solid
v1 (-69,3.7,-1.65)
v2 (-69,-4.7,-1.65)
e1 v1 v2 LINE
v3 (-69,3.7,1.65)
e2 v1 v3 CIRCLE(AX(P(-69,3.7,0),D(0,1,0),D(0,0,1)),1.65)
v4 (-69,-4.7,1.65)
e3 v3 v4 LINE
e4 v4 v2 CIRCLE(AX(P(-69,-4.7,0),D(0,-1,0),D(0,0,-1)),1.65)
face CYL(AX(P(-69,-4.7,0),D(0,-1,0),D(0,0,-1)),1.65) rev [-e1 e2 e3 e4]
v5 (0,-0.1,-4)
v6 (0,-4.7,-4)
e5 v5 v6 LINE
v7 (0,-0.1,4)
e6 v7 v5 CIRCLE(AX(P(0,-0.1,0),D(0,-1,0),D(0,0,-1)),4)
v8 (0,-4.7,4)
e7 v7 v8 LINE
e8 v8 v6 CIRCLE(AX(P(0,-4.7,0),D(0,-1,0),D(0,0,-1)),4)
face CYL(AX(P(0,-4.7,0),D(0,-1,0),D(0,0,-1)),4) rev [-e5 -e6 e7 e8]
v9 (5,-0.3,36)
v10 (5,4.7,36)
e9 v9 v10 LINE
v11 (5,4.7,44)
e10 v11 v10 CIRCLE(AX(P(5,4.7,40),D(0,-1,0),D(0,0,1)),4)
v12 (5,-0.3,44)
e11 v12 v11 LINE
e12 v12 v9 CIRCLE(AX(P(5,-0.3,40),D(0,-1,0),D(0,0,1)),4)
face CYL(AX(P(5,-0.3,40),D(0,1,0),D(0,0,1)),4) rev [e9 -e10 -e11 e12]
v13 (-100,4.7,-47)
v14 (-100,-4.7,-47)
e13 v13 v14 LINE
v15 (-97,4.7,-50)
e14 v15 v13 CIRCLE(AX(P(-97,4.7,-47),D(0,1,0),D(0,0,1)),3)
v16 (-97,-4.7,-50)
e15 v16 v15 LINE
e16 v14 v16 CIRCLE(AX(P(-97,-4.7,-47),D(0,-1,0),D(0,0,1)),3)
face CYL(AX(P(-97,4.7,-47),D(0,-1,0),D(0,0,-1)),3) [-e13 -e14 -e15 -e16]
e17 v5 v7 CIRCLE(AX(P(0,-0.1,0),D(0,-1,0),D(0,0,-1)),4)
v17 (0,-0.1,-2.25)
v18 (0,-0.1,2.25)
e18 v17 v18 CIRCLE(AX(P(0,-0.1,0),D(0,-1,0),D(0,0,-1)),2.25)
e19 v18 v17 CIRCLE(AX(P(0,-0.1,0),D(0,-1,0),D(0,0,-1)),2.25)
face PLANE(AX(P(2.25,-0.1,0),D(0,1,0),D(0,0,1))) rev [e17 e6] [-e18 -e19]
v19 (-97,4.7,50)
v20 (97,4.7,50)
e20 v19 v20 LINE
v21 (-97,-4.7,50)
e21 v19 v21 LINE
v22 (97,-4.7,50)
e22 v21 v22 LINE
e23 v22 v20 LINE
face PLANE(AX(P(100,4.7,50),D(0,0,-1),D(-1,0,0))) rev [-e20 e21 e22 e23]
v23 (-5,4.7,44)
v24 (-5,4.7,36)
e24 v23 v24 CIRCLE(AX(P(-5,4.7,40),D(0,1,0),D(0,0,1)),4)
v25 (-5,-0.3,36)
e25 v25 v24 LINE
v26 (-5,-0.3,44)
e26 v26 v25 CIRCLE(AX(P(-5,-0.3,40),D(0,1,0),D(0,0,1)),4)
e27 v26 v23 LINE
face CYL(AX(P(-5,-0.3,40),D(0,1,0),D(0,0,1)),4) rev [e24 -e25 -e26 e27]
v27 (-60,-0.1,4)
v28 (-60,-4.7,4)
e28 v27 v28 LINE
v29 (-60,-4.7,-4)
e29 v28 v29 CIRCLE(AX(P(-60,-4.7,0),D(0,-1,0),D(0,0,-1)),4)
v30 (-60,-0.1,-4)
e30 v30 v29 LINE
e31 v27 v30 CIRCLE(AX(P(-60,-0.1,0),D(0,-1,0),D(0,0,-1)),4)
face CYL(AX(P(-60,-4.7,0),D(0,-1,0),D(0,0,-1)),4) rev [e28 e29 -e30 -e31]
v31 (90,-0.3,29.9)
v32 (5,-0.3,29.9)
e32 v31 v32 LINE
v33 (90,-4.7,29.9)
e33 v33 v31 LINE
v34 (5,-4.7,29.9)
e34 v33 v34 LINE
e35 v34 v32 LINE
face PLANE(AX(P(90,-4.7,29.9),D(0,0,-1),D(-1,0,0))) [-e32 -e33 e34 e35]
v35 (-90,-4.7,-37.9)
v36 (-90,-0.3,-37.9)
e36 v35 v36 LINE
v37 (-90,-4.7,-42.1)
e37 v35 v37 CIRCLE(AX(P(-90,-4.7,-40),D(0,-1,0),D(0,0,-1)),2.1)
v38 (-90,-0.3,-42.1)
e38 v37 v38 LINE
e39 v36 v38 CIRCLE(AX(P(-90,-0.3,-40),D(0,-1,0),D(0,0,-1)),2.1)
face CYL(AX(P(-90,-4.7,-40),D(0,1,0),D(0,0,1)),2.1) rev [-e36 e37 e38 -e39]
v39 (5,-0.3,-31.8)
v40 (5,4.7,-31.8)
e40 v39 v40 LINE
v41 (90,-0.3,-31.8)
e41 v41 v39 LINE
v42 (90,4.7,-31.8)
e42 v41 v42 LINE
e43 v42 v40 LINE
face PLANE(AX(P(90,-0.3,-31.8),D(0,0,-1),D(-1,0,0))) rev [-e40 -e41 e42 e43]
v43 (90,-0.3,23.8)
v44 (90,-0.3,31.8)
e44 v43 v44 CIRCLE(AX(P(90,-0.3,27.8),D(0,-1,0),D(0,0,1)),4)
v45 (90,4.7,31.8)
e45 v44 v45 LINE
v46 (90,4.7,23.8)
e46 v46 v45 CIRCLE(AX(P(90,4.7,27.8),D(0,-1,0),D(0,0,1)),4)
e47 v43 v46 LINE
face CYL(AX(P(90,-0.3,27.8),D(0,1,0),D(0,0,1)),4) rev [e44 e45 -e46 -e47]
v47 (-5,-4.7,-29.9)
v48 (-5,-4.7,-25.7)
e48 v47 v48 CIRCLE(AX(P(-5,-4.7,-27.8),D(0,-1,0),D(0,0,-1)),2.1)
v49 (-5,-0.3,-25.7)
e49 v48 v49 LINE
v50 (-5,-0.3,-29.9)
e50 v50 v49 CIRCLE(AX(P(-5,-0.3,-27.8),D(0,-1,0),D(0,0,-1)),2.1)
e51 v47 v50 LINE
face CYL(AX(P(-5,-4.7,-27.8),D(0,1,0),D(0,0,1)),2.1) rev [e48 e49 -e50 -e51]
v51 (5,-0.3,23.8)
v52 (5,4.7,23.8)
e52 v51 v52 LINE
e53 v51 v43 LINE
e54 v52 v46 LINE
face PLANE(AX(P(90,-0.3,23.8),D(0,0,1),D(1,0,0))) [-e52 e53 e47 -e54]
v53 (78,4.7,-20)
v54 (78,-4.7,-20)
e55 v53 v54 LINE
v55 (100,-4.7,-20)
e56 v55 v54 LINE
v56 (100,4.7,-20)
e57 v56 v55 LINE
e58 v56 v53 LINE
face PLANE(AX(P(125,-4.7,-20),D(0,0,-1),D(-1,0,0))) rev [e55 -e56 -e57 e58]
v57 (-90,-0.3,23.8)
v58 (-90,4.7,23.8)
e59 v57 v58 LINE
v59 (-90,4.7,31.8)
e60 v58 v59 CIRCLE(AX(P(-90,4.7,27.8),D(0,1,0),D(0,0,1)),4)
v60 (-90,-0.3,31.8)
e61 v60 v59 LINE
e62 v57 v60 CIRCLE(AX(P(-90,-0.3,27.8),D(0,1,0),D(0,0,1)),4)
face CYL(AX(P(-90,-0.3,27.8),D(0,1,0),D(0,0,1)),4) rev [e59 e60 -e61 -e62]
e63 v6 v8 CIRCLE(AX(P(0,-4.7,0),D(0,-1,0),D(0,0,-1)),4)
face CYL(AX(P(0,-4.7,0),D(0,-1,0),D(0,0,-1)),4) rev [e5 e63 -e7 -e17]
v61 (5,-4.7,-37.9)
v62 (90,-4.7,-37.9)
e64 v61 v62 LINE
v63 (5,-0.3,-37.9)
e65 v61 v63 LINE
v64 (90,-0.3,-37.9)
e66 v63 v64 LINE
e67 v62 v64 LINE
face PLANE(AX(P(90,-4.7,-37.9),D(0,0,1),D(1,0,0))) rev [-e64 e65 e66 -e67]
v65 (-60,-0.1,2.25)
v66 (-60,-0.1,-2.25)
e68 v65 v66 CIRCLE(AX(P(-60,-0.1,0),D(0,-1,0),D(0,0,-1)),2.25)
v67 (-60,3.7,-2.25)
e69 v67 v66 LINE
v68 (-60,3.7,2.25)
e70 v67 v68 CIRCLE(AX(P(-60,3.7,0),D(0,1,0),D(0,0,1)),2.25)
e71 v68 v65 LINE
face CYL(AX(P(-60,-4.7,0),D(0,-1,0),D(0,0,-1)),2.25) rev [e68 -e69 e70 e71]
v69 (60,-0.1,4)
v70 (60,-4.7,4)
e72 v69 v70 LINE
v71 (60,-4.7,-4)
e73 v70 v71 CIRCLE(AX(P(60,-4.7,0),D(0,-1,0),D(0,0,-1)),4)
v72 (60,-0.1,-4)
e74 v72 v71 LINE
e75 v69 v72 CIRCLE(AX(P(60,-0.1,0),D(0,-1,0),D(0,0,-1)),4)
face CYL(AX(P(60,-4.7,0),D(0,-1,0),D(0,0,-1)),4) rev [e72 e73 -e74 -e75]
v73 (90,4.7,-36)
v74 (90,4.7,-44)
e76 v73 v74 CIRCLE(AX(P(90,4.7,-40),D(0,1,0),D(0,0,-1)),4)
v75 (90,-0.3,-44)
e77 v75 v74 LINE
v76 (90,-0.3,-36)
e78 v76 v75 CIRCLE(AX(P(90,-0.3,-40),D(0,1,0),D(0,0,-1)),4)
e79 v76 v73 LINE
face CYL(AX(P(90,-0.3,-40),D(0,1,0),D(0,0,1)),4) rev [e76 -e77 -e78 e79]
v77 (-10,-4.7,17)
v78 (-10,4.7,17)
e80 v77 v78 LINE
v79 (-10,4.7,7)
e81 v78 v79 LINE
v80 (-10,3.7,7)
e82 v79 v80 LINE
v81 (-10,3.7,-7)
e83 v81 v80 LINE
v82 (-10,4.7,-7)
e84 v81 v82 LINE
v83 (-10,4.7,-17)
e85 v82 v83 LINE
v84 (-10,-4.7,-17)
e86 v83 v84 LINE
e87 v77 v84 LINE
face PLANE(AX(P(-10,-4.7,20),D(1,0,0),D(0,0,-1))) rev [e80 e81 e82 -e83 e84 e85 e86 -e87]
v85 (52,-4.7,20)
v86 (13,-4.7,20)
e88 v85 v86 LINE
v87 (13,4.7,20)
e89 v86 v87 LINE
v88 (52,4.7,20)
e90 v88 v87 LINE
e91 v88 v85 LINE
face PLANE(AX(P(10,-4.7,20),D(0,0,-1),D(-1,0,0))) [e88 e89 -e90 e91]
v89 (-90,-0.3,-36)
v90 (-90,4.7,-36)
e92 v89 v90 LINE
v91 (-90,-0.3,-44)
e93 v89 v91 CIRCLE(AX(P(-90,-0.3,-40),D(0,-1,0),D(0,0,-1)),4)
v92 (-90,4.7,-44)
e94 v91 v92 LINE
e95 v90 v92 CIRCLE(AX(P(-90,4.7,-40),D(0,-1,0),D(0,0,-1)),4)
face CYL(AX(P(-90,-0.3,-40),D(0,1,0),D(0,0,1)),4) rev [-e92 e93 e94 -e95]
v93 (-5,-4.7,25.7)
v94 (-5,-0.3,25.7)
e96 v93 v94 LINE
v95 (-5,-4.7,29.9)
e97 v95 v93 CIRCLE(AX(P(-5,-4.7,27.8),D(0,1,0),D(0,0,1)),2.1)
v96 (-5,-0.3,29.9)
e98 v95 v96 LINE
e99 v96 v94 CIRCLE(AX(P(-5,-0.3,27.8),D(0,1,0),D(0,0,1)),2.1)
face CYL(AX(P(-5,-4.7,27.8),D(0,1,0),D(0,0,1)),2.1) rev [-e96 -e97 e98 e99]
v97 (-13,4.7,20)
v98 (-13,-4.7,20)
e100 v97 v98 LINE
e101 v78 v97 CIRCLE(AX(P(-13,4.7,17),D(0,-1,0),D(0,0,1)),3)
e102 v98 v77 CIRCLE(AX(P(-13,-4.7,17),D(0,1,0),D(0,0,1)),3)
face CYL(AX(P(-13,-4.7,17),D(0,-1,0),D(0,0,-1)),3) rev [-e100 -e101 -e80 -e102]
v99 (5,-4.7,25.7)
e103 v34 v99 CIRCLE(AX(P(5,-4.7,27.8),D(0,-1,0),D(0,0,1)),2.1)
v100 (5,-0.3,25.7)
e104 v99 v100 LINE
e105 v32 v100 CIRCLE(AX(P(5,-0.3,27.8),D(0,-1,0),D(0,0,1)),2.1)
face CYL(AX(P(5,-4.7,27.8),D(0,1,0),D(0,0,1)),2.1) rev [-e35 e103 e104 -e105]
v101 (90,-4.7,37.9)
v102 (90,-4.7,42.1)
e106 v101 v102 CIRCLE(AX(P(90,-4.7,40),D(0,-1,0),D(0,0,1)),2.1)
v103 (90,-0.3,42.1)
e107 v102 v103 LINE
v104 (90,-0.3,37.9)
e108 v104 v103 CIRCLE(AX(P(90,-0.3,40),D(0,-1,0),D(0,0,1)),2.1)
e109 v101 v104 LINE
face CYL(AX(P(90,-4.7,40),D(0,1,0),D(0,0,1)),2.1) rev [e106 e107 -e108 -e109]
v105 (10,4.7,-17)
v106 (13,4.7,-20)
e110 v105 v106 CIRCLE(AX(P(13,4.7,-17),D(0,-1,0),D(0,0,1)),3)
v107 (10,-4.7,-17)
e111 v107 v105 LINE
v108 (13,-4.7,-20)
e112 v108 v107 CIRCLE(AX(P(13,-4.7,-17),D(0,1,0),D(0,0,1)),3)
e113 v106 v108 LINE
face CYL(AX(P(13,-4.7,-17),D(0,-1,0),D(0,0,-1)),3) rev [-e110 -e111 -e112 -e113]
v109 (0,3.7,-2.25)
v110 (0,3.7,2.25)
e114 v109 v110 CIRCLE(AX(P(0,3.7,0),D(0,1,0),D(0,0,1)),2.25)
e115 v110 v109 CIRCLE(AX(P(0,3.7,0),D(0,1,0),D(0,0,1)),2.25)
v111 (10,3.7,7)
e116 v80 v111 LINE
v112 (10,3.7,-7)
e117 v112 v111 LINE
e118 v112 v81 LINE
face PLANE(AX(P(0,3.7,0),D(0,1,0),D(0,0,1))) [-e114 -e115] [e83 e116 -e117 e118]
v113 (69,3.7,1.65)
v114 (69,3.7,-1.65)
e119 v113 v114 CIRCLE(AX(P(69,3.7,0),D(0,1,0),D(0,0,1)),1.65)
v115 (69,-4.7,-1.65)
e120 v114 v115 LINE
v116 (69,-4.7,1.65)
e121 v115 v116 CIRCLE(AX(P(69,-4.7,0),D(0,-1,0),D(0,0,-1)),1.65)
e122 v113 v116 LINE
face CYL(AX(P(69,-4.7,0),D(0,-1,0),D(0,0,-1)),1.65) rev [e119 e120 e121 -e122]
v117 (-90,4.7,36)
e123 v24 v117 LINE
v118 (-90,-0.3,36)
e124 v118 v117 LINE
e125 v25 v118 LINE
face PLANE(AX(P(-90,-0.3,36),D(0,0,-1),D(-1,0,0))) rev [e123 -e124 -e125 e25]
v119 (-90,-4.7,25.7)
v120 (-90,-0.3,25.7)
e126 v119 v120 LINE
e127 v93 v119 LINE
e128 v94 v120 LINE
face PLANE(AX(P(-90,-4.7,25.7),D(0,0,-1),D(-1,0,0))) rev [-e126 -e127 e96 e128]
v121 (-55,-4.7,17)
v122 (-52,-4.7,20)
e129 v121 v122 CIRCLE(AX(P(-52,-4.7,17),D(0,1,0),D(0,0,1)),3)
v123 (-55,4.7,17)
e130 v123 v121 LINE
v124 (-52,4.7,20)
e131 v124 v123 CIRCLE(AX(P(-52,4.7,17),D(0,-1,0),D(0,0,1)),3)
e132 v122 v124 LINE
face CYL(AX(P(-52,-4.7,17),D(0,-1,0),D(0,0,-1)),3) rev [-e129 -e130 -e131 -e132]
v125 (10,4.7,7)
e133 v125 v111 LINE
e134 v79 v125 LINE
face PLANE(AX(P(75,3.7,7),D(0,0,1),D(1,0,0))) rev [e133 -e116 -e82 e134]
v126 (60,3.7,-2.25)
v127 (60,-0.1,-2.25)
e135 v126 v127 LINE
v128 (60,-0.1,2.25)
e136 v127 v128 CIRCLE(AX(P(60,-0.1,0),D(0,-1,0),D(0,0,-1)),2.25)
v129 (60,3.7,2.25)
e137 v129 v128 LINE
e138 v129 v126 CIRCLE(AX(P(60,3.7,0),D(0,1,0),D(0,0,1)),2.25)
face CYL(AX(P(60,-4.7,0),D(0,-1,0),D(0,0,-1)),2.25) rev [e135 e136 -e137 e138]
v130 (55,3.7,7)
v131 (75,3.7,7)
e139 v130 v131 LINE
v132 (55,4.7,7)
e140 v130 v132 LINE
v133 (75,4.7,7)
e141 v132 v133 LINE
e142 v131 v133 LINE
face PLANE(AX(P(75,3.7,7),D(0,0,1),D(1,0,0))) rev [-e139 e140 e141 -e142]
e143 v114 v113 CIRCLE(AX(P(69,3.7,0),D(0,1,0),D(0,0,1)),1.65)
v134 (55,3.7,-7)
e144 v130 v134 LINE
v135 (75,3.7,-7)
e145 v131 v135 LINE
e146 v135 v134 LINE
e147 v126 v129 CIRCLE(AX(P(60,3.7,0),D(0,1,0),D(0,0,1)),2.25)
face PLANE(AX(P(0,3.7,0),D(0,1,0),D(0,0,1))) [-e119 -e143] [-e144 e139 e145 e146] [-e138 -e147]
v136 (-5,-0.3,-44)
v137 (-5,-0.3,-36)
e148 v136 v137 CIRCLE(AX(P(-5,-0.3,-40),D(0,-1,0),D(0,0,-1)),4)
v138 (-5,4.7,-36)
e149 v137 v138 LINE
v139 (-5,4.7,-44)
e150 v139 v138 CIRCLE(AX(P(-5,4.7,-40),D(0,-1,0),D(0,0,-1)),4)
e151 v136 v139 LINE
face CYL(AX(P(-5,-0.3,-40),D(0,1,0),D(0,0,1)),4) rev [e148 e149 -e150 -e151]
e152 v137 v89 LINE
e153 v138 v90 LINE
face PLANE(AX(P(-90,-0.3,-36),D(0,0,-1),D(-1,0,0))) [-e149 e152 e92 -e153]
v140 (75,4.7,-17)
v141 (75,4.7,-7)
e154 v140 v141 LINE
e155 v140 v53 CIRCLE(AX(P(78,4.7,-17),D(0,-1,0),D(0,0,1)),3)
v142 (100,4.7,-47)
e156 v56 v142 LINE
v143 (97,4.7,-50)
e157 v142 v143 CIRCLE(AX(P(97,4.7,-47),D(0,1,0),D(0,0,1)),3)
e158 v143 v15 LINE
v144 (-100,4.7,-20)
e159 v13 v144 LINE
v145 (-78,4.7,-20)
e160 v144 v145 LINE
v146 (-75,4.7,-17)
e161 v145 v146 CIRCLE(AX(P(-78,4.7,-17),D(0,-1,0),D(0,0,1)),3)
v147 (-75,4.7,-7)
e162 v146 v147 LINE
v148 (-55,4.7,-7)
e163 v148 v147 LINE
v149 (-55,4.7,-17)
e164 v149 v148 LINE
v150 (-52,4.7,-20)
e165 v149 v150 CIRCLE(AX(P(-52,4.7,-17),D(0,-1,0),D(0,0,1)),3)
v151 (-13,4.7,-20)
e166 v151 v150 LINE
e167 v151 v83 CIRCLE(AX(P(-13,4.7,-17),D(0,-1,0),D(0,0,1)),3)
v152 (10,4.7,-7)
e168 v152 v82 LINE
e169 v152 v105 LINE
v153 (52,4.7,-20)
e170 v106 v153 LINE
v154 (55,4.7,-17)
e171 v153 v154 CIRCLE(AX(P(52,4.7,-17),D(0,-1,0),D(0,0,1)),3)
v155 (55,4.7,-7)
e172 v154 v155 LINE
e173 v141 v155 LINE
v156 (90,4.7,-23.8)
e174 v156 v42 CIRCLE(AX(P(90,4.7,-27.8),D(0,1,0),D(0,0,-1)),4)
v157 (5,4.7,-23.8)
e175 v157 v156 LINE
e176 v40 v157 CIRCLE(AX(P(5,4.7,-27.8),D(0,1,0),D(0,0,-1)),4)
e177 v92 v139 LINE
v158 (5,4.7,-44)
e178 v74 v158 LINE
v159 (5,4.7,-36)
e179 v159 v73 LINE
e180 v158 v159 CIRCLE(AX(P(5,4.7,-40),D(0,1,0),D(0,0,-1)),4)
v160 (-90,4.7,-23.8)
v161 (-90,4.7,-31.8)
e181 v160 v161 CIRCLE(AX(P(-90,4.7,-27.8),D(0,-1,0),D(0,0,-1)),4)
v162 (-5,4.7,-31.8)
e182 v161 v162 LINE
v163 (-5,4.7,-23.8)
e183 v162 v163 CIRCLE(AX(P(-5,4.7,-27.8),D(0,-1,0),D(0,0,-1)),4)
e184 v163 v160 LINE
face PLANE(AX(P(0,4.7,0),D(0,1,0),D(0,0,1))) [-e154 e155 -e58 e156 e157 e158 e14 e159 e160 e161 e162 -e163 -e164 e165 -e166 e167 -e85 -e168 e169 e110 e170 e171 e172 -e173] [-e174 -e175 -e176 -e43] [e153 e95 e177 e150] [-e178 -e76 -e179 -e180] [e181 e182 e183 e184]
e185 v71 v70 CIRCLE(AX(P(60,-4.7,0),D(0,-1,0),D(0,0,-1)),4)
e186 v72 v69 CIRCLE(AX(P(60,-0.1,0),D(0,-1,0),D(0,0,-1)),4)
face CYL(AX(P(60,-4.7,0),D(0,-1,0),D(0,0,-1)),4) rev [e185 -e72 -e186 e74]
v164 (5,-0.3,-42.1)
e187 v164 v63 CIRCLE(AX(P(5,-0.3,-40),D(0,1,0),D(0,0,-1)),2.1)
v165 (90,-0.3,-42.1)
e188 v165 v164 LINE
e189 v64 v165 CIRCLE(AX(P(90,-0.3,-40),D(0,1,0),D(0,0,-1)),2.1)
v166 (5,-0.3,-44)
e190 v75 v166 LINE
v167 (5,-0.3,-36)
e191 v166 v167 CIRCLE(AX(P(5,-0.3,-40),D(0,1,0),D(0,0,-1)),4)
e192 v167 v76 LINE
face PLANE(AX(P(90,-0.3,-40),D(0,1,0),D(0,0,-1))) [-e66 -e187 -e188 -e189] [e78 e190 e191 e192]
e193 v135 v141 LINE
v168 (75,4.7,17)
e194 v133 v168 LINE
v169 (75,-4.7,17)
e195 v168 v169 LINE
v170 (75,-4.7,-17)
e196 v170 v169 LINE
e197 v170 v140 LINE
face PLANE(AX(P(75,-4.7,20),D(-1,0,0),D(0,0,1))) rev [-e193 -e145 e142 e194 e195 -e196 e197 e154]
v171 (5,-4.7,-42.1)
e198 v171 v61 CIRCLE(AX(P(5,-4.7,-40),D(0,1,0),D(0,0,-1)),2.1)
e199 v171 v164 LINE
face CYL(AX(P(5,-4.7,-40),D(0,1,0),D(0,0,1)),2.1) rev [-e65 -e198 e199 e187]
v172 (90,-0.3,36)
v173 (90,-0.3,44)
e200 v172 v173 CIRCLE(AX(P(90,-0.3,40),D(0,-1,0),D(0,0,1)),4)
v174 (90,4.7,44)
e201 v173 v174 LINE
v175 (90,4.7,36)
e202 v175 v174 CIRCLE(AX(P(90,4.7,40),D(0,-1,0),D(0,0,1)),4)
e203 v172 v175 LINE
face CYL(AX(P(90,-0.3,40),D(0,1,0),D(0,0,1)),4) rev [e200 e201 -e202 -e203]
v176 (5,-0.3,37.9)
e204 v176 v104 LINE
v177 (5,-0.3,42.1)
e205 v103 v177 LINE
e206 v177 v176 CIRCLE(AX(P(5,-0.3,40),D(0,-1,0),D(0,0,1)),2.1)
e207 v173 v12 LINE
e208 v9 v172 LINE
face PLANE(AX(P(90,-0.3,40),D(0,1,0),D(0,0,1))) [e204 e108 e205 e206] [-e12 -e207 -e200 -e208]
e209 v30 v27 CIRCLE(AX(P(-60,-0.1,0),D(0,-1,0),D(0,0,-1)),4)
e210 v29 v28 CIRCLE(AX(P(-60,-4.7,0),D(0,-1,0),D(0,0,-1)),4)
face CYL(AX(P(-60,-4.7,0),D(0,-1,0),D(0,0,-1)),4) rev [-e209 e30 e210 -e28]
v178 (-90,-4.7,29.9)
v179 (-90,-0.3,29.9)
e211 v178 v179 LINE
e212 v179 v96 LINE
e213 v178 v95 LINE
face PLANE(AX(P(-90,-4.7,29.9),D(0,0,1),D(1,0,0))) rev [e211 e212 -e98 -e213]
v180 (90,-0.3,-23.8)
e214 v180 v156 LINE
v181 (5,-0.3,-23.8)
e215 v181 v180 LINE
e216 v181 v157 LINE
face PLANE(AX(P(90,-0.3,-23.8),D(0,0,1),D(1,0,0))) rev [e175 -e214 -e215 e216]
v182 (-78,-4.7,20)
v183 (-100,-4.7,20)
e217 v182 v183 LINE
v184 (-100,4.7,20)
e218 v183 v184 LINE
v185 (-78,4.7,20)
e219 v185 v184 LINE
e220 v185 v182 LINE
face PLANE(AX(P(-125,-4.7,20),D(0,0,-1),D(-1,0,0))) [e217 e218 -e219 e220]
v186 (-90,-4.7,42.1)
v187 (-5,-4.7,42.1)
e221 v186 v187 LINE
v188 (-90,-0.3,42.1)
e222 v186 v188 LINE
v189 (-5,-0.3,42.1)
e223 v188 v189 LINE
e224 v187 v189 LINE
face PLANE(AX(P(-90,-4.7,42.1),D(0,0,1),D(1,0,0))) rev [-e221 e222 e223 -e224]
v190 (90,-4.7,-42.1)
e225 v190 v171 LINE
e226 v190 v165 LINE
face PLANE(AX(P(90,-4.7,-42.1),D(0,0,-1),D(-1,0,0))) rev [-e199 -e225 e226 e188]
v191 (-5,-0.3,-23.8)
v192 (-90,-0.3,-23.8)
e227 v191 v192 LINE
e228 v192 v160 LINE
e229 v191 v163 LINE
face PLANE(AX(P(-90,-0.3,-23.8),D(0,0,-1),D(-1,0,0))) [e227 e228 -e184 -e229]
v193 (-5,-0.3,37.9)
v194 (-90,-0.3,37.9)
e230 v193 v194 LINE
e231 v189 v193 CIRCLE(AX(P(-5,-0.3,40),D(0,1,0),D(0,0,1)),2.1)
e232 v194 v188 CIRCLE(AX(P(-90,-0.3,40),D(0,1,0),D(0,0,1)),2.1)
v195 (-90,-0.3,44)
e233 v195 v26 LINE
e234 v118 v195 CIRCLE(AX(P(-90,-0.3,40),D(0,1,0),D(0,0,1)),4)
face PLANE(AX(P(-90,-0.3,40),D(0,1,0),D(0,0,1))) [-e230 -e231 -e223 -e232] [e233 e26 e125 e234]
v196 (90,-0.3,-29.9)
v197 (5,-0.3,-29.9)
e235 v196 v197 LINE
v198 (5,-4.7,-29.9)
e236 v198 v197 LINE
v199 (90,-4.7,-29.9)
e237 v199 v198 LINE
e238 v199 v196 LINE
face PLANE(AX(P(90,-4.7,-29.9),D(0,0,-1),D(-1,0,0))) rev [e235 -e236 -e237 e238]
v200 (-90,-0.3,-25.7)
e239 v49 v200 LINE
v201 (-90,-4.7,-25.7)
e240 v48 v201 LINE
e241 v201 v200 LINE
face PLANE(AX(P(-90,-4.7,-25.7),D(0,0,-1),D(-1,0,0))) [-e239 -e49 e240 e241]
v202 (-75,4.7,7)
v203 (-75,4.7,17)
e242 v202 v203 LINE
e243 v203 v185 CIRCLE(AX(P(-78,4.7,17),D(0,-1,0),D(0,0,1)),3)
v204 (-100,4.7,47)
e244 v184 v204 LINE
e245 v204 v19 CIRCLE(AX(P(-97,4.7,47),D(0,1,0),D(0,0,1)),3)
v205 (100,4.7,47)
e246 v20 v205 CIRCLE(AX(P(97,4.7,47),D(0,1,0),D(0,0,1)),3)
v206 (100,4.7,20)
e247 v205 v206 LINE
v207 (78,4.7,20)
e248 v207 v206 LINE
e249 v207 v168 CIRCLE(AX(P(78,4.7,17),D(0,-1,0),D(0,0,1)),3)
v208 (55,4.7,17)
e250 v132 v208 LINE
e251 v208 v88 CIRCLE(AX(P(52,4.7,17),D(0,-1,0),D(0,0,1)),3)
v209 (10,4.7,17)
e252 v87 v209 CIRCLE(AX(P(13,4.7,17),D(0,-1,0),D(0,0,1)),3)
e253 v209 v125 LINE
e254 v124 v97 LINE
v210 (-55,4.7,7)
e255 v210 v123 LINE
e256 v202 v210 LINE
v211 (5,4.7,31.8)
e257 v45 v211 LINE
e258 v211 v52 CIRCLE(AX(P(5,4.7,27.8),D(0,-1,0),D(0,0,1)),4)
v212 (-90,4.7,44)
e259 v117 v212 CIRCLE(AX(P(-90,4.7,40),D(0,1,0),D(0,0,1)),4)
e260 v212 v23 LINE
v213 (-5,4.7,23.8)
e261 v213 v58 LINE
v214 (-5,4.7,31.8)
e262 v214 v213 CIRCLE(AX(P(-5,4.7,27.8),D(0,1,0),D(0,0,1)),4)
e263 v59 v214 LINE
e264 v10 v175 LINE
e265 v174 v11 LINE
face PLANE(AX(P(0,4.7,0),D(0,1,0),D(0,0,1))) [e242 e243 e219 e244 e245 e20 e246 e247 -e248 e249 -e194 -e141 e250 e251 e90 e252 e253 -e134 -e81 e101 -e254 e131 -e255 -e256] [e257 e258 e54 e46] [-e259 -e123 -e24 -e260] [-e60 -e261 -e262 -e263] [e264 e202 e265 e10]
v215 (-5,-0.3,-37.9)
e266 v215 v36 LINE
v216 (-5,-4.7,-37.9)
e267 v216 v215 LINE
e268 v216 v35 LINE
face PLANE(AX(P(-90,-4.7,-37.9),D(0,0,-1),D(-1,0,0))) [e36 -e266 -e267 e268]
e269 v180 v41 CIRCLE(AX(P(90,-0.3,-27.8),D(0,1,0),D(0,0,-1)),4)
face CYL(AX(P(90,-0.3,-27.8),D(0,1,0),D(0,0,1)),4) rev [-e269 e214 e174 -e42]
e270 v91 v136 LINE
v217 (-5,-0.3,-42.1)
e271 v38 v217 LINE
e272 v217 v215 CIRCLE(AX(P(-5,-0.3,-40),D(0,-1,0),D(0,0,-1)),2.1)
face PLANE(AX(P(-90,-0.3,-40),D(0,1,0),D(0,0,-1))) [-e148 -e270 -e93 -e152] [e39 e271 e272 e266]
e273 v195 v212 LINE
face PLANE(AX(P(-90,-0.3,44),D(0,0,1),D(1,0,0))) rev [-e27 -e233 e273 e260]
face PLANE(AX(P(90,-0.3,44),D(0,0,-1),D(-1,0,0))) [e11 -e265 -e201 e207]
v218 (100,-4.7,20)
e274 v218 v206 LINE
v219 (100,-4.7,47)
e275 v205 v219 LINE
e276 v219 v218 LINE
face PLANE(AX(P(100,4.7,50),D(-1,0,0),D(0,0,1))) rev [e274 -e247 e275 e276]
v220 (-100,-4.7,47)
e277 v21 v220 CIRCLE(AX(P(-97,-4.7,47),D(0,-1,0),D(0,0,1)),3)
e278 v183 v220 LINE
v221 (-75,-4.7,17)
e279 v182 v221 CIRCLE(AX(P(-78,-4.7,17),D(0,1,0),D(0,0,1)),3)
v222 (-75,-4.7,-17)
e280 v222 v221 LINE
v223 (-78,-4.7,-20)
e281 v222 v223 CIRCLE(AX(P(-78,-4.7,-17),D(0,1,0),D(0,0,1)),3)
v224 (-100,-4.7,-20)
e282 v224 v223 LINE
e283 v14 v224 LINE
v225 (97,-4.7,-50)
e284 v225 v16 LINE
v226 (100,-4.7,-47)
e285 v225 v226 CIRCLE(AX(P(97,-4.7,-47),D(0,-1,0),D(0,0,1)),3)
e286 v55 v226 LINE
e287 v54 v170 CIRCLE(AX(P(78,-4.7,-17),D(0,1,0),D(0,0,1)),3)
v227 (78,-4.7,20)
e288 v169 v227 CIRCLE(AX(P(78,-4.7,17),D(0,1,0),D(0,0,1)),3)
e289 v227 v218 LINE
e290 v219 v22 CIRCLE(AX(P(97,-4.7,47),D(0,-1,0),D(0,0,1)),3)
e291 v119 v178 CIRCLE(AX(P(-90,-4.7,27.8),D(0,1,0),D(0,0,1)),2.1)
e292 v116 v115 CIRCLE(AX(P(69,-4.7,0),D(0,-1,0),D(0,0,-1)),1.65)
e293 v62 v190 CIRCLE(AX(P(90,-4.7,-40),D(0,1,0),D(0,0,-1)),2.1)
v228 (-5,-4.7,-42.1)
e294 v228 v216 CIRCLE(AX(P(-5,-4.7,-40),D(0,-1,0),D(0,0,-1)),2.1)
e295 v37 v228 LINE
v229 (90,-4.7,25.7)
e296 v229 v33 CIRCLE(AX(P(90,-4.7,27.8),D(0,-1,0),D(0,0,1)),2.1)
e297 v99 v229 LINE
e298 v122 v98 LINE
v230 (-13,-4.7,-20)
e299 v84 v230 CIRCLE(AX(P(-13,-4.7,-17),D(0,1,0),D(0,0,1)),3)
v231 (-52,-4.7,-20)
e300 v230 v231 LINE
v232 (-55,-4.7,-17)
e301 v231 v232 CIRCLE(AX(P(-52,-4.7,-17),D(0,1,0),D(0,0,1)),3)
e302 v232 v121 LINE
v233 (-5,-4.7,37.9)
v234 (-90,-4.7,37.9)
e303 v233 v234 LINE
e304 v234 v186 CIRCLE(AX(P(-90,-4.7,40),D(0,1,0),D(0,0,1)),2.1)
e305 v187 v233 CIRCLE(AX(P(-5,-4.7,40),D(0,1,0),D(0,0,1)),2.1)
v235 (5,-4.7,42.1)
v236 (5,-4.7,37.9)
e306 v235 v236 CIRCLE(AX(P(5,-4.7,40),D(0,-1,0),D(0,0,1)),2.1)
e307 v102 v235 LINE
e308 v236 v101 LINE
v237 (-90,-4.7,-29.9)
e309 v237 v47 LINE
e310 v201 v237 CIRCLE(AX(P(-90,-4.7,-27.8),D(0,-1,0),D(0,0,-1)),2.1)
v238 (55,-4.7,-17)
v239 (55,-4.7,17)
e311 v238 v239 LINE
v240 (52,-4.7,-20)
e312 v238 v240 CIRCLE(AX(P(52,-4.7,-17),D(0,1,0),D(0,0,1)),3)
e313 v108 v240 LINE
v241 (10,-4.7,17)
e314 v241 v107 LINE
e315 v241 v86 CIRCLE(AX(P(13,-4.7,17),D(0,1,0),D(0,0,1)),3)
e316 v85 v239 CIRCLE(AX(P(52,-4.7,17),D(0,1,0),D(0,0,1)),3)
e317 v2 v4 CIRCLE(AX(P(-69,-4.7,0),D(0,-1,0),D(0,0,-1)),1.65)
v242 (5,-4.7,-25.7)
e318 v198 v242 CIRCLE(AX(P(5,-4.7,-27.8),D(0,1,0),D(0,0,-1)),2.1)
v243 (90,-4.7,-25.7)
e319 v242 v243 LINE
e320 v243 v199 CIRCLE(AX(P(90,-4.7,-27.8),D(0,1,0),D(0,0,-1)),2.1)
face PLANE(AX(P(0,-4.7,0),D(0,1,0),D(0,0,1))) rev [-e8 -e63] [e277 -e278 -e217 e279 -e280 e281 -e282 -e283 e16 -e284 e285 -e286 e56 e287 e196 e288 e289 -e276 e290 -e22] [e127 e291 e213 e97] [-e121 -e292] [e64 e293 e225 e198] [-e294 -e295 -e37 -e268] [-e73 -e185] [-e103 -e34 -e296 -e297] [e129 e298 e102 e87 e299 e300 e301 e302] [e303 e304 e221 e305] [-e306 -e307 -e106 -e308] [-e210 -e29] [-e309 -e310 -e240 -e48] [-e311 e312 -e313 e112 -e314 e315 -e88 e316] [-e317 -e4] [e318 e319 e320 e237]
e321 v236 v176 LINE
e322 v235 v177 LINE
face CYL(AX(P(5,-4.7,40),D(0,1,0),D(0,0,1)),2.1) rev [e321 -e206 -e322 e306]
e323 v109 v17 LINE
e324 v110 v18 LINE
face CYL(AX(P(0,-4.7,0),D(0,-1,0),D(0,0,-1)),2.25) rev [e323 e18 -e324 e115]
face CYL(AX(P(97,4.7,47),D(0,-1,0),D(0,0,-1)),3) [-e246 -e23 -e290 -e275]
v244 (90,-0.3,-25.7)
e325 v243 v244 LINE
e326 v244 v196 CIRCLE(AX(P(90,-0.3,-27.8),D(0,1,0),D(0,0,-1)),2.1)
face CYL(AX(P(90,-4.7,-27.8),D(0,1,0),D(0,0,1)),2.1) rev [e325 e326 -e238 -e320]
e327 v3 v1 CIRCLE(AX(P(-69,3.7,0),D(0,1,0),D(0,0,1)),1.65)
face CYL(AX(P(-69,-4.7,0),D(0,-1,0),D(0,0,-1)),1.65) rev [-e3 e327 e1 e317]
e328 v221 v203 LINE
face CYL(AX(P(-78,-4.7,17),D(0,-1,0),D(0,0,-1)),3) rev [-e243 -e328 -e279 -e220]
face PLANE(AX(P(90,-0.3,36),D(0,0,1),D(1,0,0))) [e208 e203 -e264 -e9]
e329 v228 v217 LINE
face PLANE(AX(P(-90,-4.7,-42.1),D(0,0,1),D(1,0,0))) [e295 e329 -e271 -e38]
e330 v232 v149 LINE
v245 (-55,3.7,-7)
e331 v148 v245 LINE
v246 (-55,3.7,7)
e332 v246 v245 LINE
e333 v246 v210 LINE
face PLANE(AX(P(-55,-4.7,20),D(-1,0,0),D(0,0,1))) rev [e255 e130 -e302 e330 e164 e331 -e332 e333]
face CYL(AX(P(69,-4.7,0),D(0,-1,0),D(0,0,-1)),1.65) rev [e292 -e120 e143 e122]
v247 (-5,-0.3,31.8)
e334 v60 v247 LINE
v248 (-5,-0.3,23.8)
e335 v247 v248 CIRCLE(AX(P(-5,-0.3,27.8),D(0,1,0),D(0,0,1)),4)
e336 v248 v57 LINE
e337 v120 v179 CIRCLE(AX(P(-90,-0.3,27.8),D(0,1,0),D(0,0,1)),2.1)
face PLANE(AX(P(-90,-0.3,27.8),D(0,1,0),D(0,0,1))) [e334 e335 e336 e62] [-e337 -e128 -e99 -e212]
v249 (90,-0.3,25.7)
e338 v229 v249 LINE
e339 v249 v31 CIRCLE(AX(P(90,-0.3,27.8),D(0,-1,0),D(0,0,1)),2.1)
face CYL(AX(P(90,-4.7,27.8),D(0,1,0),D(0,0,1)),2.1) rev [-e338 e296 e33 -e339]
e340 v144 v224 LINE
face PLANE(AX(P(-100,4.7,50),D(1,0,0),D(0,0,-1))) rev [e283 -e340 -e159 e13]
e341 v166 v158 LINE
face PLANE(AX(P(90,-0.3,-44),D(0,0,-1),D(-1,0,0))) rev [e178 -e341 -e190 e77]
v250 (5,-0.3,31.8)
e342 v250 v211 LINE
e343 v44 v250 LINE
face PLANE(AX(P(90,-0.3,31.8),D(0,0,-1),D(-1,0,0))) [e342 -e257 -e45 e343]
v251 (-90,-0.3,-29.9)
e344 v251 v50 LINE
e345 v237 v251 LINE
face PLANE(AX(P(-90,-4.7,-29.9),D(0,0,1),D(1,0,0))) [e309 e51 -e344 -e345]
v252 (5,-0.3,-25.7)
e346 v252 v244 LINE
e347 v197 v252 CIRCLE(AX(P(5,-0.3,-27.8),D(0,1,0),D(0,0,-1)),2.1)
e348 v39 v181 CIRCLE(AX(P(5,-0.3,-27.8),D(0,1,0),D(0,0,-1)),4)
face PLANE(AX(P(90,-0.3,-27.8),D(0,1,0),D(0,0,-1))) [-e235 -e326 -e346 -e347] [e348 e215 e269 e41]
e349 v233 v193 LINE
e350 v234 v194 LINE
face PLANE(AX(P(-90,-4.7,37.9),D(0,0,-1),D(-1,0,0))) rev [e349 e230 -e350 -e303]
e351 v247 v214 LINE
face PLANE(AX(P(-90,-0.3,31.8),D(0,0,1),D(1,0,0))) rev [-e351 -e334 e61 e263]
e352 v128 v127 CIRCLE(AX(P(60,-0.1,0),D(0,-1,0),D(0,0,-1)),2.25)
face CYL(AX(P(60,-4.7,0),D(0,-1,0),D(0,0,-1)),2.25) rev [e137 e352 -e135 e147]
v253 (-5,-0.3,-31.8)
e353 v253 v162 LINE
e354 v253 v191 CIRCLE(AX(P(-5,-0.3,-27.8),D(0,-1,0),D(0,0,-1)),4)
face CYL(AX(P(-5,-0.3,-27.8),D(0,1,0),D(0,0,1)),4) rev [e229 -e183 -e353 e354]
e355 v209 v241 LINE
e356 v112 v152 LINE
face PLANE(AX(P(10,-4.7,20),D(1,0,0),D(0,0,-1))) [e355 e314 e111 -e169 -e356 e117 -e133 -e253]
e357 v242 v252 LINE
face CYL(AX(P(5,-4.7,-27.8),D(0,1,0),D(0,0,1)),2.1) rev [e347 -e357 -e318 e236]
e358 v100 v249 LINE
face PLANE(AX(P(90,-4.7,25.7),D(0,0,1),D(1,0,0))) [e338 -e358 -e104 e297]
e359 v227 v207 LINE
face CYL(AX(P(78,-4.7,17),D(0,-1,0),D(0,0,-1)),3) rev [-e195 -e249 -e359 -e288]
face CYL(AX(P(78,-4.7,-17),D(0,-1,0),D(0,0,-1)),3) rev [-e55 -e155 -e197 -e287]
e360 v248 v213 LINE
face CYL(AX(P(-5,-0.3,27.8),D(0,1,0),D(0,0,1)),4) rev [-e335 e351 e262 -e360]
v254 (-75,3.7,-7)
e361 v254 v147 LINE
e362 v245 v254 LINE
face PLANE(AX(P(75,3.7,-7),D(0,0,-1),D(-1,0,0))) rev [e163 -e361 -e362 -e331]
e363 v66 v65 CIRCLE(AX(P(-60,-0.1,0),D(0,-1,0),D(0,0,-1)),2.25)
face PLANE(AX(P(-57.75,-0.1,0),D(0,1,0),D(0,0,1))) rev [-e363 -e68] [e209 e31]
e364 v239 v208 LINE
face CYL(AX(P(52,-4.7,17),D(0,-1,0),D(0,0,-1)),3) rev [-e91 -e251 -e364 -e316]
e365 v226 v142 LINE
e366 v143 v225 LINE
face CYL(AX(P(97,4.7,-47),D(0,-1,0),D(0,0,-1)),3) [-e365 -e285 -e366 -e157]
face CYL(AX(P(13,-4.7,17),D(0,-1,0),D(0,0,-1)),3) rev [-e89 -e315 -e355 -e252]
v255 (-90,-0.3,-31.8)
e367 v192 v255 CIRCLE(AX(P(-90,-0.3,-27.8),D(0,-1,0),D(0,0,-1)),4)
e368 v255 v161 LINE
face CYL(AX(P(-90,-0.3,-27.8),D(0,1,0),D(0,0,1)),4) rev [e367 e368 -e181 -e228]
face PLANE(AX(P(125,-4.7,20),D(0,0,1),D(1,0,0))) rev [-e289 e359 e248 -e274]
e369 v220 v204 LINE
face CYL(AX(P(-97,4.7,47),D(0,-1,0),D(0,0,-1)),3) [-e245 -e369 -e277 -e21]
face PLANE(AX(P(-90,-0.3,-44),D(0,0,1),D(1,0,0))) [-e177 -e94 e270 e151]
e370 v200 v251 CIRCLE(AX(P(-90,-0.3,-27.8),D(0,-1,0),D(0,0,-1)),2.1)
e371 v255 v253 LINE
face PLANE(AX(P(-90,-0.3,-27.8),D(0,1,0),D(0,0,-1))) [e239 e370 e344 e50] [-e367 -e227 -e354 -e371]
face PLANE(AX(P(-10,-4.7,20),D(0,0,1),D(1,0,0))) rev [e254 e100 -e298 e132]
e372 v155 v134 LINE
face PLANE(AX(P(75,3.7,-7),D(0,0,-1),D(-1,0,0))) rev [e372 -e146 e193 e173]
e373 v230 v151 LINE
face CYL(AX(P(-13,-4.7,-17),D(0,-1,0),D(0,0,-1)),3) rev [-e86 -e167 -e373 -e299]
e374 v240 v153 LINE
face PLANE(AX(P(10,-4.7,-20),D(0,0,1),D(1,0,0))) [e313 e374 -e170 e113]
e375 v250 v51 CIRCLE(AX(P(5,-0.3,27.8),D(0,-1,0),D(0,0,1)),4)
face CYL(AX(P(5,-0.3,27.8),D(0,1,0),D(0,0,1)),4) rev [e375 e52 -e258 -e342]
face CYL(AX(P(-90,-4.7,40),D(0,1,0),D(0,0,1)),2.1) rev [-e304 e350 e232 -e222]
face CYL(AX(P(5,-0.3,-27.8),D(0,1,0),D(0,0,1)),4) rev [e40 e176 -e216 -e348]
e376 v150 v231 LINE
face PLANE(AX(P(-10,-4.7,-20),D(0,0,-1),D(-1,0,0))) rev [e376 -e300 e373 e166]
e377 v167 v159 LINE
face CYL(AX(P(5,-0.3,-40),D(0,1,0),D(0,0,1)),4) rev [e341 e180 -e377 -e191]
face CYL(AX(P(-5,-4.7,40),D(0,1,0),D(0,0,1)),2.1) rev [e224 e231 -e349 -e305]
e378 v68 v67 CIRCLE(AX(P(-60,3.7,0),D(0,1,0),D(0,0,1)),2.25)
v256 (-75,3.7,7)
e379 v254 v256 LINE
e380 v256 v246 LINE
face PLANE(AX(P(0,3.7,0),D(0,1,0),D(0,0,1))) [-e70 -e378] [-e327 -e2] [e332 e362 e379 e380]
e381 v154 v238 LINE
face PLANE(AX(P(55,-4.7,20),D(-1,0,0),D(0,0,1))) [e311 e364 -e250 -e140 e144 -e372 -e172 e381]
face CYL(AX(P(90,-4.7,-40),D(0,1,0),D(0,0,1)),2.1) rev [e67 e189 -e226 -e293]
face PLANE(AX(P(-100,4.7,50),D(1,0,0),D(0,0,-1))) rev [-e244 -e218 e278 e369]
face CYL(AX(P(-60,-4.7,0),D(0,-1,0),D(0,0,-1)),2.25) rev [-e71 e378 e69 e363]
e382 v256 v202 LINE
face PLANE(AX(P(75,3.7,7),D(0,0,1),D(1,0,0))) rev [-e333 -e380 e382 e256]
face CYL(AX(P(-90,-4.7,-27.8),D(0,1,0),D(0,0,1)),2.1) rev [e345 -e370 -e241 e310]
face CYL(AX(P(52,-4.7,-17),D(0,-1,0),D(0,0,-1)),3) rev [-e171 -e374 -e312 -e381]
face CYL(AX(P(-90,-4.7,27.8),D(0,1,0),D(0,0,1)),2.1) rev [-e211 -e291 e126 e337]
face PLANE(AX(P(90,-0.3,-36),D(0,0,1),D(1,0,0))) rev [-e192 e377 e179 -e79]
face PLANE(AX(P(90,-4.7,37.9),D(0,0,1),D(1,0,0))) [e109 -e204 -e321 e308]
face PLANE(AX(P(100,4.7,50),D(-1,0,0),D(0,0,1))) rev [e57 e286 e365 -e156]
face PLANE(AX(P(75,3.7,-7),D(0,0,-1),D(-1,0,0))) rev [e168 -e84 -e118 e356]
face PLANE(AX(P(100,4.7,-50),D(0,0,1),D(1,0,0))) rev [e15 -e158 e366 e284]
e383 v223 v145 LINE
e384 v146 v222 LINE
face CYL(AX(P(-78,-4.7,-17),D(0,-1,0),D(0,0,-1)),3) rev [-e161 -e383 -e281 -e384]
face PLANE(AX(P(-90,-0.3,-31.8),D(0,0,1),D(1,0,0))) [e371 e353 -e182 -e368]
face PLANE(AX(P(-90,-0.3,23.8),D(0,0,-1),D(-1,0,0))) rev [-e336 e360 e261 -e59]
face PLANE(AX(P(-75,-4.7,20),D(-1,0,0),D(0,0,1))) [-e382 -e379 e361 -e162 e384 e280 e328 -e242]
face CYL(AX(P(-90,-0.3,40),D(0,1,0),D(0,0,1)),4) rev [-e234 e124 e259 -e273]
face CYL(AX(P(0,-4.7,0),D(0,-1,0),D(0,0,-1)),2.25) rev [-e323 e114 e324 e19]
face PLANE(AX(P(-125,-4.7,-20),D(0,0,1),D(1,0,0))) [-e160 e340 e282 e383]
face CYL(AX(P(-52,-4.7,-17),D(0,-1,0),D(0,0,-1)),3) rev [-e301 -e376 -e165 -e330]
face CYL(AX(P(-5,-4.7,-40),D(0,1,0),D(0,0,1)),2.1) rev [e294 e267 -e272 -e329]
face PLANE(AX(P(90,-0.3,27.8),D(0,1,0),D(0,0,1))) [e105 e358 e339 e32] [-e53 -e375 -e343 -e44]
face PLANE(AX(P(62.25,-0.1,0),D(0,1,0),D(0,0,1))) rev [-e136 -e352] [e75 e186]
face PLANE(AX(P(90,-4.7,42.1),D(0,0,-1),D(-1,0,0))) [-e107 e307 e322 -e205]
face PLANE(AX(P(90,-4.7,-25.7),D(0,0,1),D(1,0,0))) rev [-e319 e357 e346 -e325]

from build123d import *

# Parameters (mm, degrees)
SKETCH1_W                                            = 200
SKETCH1_H                                            = 100
BOSS_EXTRUDE1_DEPTH                                  = 4.7
FILLET1_R                                            = 3
SKETCH2_W                                            = 50
SKETCH2_H                                            = 40
CUT_EXTRUDE1_DEPTH                                   = 113.197860942
SKETCH3_W                                            = 45
SKETCH3_H                                            = 40
CUT_EXTRUDE2_DEPTH                                   = 113.197860942
FILLET2_R                                            = 3
FILLET3_R                                            = 3
FILLET3_OF_MIRROR2_R                                 = 3
CUT_EXTRUDE3_DEPTH                                   = 5
CUT_EXTRUDE4_DEPTH                                   = 112.915146428
MIRROR3_AT_THE_SECOND_PLANE_COPY_1_DEPTH             = 5
MIRROR3_AT_THE_SECOND_PLANE_COPY_2_DEPTH             = 112.915146428
SKETCH6_W                                            = 150
SKETCH6_H                                            = 14
CUT_EXTRUDE5_DEPTH                                   = 1
M4_TAPPED_HOLE1_D                                    = 3.3
M4_TAPPED_HOLE1_DEPTH                                = 11.5
M4_TAPPED_HOLE1_TIP                                  = 0.991420021
CBORE_FOR_M4_HEXAGON_SOCKET_HEAD_CAP_SCR_D           = 4.5
CBORE_FOR_M4_HEXAGON_SOCKET_HEAD_CAP_SCR_DEPTH       = 11.5
CBORE_FOR_M4_HEXAGON_SOCKET_HEAD_CAP_SCR_CBORE_D     = 8
CBORE_FOR_M4_HEXAGON_SOCKET_HEAD_CAP_SCR_CBORE_DEPTH = 4.6
CBORE_FOR_M4_HEXAGON_SOCKET_HEAD_CAP_SCR_TIP         = 1.351936393


with BuildPart() as part:
    # Sketch1 → Boss-Extrude1 (new, symmetric)
    with BuildSketch(Plane(origin=(0, 0, 0), x_dir=(1, 0, 0), z_dir=(0, 1, 0))):
        Rectangle(SKETCH1_W, SKETCH1_H)
    extrude(amount=BOSS_EXTRUDE1_DEPTH, both=True)

    # Fillet1
    fillet1_edges = [part.edges().sort_by_distance(p)[0] for p in [
        (-100, 0, -50),
        (100, 0, -50),
        (100, 0, 50),
        (-100, 0, 50),
    ]]
    fillet(fillet1_edges, radius=FILLET1_R)

    # Sketch2 → Cut-Extrude1 (cut, through all)
    with BuildSketch(Plane(origin=(0, 4.7, 0), x_dir=(1, 0, 0), z_dir=(0, 1, 0))):
        with Locations((100, 0)):
            Rectangle(SKETCH2_W, SKETCH2_H)
    cut_extrude1 = extrude(amount=-CUT_EXTRUDE1_DEPTH, mode=Mode.SUBTRACT)

    # Mirror1: Cut-Extrude1 across plane
    add(cut_extrude1.mirror(Plane(origin=(0, 0, 0), x_dir=(0, 0, 1), z_dir=(1, 0, 0))), mode=Mode.SUBTRACT)

    # Sketch3 → Cut-Extrude2 (cut, through all)
    with BuildSketch(Plane(origin=(0, 4.7, 0), x_dir=(1, 0, 0), z_dir=(0, 1, 0))):
        with Locations((-32.5, 0)):
            Rectangle(SKETCH3_W, SKETCH3_H)
    cut_extrude2 = extrude(amount=-CUT_EXTRUDE2_DEPTH, mode=Mode.SUBTRACT)

    # Fillet2
    fillet2_edges = [part.edges().sort_by_distance(p)[0] for p in [
        (75, 0, -20),
        (75, 0, 20),
        (-75, 0, 20),
        (-75, 0, -20),
    ]]
    fillet(fillet2_edges, radius=FILLET2_R)

    # Fillet3
    fillet3_edges = [part.edges().sort_by_distance(p)[0] for p in [
        (-55, 0, 20),
        (-55, 0, -20),
        (-10, 0, -20),
        (-10, 0, 20),
    ]]
    fillet(fillet3_edges, radius=FILLET3_R)

    # Mirror2: Cut-Extrude2 across plane
    add(cut_extrude2.mirror(Plane(origin=(0, 0, 0), x_dir=(0, 0, 1), z_dir=(1, 0, 0))), mode=Mode.SUBTRACT)

    # Fillet3 of Mirror2
    fillet3_of_mirror2_edges = [part.edges().sort_by_distance(p)[0] for p in [
        (55, 0, 20),
        (55, 0, -20),
        (10, 0, -20),
        (10, 0, 20),
    ]]
    fillet(fillet3_of_mirror2_edges, radius=FILLET3_OF_MIRROR2_R)

    # Sketch4 → Cut-Extrude3 (cut)
    with BuildSketch(Plane(origin=(0, 4.7, 0), x_dir=(1, 0, 0), z_dir=(0, 1, 0))):
        with BuildLine():
            Line((-90, -36), (-5, -36))
            ThreePointArc((-5, -36), (-1, -40), (-5, -44))
            Line((-5, -44), (-90, -44))
            ThreePointArc((-90, -44), (-94, -40), (-90, -36))
        make_face()
        with BuildLine():
            Line((-90, -31.8), (-5, -31.8))
            ThreePointArc((-5, -31.8), (-1, -27.8), (-5, -23.8))
            Line((-5, -23.8), (-90, -23.8))
            ThreePointArc((-90, -23.8), (-94, -27.8), (-90, -31.8))
        make_face()
    cut_extrude3 = extrude(amount=-CUT_EXTRUDE3_DEPTH, mode=Mode.SUBTRACT)

    # Sketch5 → Cut-Extrude4 (cut, through all)
    with BuildSketch(Plane(origin=(0, -0.3, 0), x_dir=(1, 0, 0), z_dir=(0, 1, 0))):
        with BuildLine():
            Line((-90, -25.7), (-5, -25.7))
            ThreePointArc((-5, -25.7), (-2.9, -27.8), (-5, -29.9))
            Line((-5, -29.9), (-90, -29.9))
            ThreePointArc((-90, -29.9), (-92.1, -27.8), (-90, -25.7))
        make_face()
        with BuildLine():
            Line((-90, -37.9), (-5, -37.9))
            ThreePointArc((-5, -37.9), (-2.9, -40), (-5, -42.1))
            Line((-5, -42.1), (-90, -42.1))
            ThreePointArc((-90, -42.1), (-92.1, -40), (-90, -37.9))
        make_face()
    cut_extrude4 = extrude(amount=-CUT_EXTRUDE4_DEPTH, mode=Mode.SUBTRACT)

    # Mirror3: Cut-Extrude3, Cut-Extrude4 across plane
    add(cut_extrude3.mirror(Plane(origin=(0, 0, 0), x_dir=(0, 0, 1), z_dir=(1, 0, 0))), mode=Mode.SUBTRACT)
    add(cut_extrude4.mirror(Plane(origin=(0, 0, 0), x_dir=(0, 0, 1), z_dir=(1, 0, 0))), mode=Mode.SUBTRACT)

    # Mirror3 at the second plane: Cut-Extrude3, Cut-Extrude4 across plane
    add(cut_extrude3.mirror(Plane.XY), mode=Mode.SUBTRACT)
    add(cut_extrude4.mirror(Plane.XY), mode=Mode.SUBTRACT)

    # Mirror3 at the second plane copy 1 sketc → Mirror3 at the second plane copy 1 (cut)
    with BuildSketch(Plane(origin=(0, 4.7, 0), x_dir=(-1, 0, 0), z_dir=(0, 1, 0))):
        with BuildLine():
            Line((-90, -36), (-5, -36))
            ThreePointArc((-5, -36), (-1, -40), (-5, -44))
            Line((-5, -44), (-90, -44))
            ThreePointArc((-90, -44), (-94, -40), (-90, -36))
        make_face()
        with BuildLine():
            Line((-90, -31.8), (-5, -31.8))
            ThreePointArc((-5, -31.8), (-1, -27.8), (-5, -23.8))
            Line((-5, -23.8), (-90, -23.8))
            ThreePointArc((-90, -23.8), (-94, -27.8), (-90, -31.8))
        make_face()
    extrude(amount=-MIRROR3_AT_THE_SECOND_PLANE_COPY_1_DEPTH, mode=Mode.SUBTRACT)

    # Mirror3 at the second plane copy 2 sketc → Mirror3 at the second plane copy 2 (cut, through all)
    with BuildSketch(Plane(origin=(0, -0.3, 0), x_dir=(-1, 0, 0), z_dir=(0, 1, 0))):
        with BuildLine():
            Line((-90, -25.7), (-5, -25.7))
            ThreePointArc((-5, -25.7), (-2.9, -27.8), (-5, -29.9))
            Line((-5, -29.9), (-90, -29.9))
            ThreePointArc((-90, -29.9), (-92.1, -27.8), (-90, -25.7))
        make_face()
        with BuildLine():
            Line((-90, -37.9), (-5, -37.9))
            ThreePointArc((-5, -37.9), (-2.9, -40), (-5, -42.1))
            Line((-5, -42.1), (-90, -42.1))
            ThreePointArc((-90, -42.1), (-92.1, -40), (-90, -37.9))
        make_face()
    extrude(amount=-MIRROR3_AT_THE_SECOND_PLANE_COPY_2_DEPTH, mode=Mode.SUBTRACT)

    # Sketch6 → Cut-Extrude5 (cut)
    with BuildSketch(Plane(origin=(0, 4.7, 0), x_dir=(1, 0, 0), z_dir=(0, 1, 0))):
        Rectangle(SKETCH6_W, SKETCH6_H)
    extrude(amount=-CUT_EXTRUDE5_DEPTH, mode=Mode.SUBTRACT)

    # M4 Tapped Hole1
    with Locations(Plane(origin=(0, -4.7, 0), x_dir=(-1, 0, 0), z_dir=(0, -1, 0))):
        with Locations((-69, 0), (69, 0)):
            Hole(M4_TAPPED_HOLE1_D / 2, depth=M4_TAPPED_HOLE1_DEPTH)
            with Locations((0, 0, -(M4_TAPPED_HOLE1_DEPTH + M4_TAPPED_HOLE1_TIP / 2))):  # 118° drill point
                Cone(0, M4_TAPPED_HOLE1_D / 2, M4_TAPPED_HOLE1_TIP, mode=Mode.SUBTRACT)

    # CBORE for M4 Hexagon socket head cap screws1
    with Locations(Plane(origin=(0, -4.7, 0), x_dir=(-1, 0, 0), z_dir=(0, -1, 0))):
        with Locations((-60, 0), (0, 0), (60, 0)):
            CounterBoreHole(CBORE_FOR_M4_HEXAGON_SOCKET_HEAD_CAP_SCR_D / 2, CBORE_FOR_M4_HEXAGON_SOCKET_HEAD_CAP_SCR_CBORE_D / 2, CBORE_FOR_M4_HEXAGON_SOCKET_HEAD_CAP_SCR_CBORE_DEPTH, depth=CBORE_FOR_M4_HEXAGON_SOCKET_HEAD_CAP_SCR_DEPTH)
            with Locations((0, 0, -(CBORE_FOR_M4_HEXAGON_SOCKET_HEAD_CAP_SCR_DEPTH + CBORE_FOR_M4_HEXAGON_SOCKET_HEAD_CAP_SCR_TIP / 2))):  # 118° drill point
                Cone(0, CBORE_FOR_M4_HEXAGON_SOCKET_HEAD_CAP_SCR_D / 2, CBORE_FOR_M4_HEXAGON_SOCKET_HEAD_CAP_SCR_TIP, mode=Mode.SUBTRACT)


solid = part.part
